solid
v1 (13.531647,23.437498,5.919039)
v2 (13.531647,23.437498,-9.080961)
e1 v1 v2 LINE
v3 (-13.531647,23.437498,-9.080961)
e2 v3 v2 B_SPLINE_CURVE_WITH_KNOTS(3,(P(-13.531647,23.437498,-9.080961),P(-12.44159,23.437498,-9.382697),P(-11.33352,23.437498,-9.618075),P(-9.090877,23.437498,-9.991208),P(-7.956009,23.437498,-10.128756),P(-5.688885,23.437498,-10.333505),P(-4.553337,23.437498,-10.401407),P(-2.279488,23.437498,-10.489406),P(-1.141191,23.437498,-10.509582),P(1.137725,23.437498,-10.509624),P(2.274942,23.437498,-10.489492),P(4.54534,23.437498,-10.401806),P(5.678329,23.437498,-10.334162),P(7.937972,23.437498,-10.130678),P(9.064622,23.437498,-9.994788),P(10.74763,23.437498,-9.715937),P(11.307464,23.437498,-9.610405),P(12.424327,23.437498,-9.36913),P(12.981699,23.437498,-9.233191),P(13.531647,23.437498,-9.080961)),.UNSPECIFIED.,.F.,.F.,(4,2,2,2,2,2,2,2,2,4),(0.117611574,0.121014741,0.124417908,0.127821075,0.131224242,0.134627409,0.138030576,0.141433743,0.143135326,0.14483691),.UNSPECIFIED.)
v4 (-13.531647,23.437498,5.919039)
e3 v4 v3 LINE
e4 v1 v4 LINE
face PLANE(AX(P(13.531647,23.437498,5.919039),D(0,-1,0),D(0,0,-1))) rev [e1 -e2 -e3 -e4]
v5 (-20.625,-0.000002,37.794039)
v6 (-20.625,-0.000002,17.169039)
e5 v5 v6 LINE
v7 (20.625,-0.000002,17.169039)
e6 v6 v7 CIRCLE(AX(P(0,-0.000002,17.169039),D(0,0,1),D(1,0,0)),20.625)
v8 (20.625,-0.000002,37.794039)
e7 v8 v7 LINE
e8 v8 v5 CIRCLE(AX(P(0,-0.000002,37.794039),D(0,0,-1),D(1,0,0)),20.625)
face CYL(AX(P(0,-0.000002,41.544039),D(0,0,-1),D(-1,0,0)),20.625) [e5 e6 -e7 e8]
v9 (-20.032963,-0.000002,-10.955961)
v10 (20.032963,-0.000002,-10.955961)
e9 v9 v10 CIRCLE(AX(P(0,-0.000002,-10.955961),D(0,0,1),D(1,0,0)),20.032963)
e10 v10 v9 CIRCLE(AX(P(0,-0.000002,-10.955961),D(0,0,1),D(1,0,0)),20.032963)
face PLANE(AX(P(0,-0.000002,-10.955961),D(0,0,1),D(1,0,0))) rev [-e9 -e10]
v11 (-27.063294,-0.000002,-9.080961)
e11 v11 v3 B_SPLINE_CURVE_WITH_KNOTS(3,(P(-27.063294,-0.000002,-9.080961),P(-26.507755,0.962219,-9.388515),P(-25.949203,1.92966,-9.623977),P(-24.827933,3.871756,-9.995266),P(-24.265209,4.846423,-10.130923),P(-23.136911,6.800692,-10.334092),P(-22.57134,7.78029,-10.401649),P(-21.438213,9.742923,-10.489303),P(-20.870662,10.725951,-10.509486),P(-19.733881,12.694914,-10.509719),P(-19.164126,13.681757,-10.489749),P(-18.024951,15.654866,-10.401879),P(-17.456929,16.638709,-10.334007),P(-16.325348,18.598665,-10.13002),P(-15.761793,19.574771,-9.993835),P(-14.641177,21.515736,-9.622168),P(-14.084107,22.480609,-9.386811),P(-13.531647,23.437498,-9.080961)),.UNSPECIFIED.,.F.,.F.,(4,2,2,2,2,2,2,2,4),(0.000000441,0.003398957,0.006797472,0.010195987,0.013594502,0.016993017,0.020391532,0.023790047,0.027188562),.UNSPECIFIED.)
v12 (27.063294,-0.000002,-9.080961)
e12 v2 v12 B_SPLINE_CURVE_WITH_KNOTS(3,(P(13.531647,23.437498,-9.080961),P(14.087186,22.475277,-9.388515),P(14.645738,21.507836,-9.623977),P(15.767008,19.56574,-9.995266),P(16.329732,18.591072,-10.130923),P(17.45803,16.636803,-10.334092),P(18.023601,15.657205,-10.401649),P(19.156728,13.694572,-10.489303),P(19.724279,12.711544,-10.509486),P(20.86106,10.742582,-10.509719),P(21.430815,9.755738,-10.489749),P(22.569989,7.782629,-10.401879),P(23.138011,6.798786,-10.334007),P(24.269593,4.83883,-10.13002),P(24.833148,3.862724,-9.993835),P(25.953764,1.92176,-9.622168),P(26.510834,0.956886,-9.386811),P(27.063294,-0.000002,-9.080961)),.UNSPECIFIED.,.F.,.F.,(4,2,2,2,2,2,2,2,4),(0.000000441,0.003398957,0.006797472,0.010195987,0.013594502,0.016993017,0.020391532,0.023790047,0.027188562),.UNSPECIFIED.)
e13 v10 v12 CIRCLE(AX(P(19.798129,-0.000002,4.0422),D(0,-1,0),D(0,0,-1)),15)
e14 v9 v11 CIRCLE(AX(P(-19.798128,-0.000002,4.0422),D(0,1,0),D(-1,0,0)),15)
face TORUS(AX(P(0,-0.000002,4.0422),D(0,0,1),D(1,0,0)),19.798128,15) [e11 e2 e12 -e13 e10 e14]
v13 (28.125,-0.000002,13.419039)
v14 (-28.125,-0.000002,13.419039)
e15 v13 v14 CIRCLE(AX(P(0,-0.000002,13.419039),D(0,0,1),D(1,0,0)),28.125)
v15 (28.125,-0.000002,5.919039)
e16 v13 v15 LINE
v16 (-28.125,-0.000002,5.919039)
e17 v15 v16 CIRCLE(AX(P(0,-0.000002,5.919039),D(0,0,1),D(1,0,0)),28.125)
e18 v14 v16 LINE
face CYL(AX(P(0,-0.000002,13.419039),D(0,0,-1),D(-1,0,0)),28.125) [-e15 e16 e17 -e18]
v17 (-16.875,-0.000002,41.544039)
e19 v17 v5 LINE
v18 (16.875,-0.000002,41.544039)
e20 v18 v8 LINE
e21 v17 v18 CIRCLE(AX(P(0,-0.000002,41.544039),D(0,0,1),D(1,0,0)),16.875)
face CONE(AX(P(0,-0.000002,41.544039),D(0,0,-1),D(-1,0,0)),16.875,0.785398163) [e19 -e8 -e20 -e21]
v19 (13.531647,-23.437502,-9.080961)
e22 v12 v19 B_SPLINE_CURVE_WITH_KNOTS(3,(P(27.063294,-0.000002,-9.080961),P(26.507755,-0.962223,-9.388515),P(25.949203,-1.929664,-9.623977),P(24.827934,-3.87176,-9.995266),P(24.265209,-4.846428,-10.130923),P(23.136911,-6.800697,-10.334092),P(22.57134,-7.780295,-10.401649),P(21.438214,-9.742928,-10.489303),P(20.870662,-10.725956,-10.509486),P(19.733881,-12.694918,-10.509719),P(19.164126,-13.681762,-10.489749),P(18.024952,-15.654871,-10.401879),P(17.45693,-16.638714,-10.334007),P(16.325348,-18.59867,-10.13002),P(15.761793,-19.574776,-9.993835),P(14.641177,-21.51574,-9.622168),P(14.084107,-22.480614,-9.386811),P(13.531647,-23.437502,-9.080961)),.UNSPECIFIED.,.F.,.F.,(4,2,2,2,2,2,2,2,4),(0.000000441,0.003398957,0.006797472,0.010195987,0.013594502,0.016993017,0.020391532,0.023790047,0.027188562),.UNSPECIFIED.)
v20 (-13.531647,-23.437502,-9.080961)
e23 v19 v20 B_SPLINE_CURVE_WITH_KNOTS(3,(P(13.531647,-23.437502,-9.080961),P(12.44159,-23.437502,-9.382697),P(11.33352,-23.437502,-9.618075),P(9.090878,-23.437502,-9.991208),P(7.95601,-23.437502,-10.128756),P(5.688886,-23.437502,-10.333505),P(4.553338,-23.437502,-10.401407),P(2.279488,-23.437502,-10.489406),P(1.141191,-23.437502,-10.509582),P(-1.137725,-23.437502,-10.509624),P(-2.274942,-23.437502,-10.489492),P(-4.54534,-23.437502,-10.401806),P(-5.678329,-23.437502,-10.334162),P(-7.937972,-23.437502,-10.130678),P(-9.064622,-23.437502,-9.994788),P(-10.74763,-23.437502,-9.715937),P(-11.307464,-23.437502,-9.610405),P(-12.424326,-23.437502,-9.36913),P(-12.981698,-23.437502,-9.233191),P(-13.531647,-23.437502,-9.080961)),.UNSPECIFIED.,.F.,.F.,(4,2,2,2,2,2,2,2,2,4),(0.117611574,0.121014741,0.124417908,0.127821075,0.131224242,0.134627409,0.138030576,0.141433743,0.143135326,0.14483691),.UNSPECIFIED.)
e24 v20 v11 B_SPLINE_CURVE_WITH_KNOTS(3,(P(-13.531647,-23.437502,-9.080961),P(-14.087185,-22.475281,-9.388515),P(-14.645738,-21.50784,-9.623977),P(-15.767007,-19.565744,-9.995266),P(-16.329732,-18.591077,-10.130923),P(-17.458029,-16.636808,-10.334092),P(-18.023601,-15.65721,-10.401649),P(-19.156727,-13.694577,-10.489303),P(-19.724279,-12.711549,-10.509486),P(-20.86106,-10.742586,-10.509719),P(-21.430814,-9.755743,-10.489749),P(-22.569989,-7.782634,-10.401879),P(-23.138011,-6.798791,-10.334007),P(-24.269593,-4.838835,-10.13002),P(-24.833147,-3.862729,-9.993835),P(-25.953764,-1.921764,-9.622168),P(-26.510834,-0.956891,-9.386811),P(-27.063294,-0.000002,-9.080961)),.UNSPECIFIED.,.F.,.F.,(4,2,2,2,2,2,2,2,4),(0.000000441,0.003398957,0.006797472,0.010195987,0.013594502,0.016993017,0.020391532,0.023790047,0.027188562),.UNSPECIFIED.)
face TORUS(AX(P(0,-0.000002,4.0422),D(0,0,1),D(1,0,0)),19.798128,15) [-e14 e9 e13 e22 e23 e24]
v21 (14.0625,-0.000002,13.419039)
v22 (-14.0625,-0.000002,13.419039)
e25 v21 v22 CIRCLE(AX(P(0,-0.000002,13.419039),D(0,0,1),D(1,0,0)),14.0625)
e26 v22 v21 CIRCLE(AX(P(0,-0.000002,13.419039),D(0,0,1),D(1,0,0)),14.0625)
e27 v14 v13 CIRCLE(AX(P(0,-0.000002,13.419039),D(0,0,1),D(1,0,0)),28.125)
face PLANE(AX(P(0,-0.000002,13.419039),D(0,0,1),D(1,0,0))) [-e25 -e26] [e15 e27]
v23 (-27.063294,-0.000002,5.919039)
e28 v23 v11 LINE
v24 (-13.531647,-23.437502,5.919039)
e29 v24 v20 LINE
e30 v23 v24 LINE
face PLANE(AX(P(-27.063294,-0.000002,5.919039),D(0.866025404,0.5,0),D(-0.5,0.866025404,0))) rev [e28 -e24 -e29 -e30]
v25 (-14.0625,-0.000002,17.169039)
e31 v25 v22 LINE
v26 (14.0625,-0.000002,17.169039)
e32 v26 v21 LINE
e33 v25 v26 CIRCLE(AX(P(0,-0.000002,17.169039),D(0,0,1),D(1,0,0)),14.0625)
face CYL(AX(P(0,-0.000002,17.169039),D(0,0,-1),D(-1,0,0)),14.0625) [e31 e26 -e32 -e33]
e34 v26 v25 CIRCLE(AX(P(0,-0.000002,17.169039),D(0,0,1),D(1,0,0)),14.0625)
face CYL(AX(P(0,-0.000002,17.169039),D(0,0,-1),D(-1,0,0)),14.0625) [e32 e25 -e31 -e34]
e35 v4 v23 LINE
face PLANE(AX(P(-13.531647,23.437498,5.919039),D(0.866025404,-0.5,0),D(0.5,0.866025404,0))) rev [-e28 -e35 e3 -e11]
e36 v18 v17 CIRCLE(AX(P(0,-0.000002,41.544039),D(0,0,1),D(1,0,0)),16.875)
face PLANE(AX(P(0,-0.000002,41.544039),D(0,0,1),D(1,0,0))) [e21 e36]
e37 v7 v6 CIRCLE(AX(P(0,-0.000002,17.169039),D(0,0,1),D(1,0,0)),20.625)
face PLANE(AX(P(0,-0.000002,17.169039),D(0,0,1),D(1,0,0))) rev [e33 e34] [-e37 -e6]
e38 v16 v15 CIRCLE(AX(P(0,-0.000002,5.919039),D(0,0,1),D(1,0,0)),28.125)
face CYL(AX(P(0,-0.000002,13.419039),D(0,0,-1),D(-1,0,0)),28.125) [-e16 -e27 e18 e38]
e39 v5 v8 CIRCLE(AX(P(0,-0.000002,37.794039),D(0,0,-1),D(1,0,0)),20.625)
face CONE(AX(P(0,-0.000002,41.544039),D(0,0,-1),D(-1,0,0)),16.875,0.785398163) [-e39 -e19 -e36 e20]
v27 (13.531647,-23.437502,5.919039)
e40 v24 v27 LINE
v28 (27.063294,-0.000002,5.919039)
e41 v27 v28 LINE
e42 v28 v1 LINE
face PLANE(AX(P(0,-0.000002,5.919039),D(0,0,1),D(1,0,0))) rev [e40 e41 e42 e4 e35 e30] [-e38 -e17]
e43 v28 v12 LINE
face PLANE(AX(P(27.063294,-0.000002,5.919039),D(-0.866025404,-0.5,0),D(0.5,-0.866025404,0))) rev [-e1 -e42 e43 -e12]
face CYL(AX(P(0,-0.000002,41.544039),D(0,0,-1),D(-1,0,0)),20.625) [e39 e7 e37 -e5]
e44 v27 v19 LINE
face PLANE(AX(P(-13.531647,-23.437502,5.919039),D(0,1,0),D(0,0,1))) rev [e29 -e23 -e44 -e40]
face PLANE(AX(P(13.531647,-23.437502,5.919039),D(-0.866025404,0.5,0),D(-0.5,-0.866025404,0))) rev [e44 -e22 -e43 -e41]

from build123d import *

# Parameters (mm, degrees)
BOSS_EXTRUDE1_DEPTH = 9
SKETCH2_R           = 15
BOSS_EXTRUDE2_DEPTH = 4
SKETCH3_R           = 7.5
BOSS_EXTRUDE3_DEPTH = 2
SKETCH4_R           = 11
BOSS_EXTRUDE5_DEPTH = 13
CHAMFER1_SIZE       = 2
SCALE_1_SCALE       = 1.875


with BuildPart() as part:
    # Sketch1 → Boss-Extrude1 (new body)
    with BuildSketch(Plane.XY):
        Polygon((14.43375673, 0), (7.216878365, 12.5), (-7.216878365, 12.5), (-14.43375673, 0), (-7.216878365, -12.5), (7.216878365, -12.5), align=None)
    extrude(amount=BOSS_EXTRUDE1_DEPTH)

    # Sketch2 → Boss-Extrude2 (add)
    with BuildSketch(Plane.XY.offset(9)):
        Circle(SKETCH2_R)
    extrude(amount=BOSS_EXTRUDE2_DEPTH)

    # Sketch3 → Boss-Extrude3 (add)
    with BuildSketch(Plane.XY.offset(13)):
        Circle(SKETCH3_R)
    extrude(amount=BOSS_EXTRUDE3_DEPTH)

    # Sketch4 → Boss-Extrude5 (add)
    with BuildSketch(Plane.XY.offset(15)):
        with Locations(Location((0, 0, 0), (0, 0, 180))):
            Circle(SKETCH4_R)
    extrude(amount=BOSS_EXTRUDE5_DEPTH)

    # Chamfer1
    chamfer1_edges = [part.edges().sort_by_distance(p)[0] for p in [
        (11, 0, 28),
    ]]
    chamfer(chamfer1_edges, length=CHAMFER1_SIZE)

    # Sketch6 → Cut-Revolve4 (revolve, cut)
    with BuildSketch(Plane(origin=(0, 0, 0), x_dir=(1, 0, 0), z_dir=(0, 1, 0)), mode=Mode.PRIVATE) as cut_revolve4_sk:
        with BuildLine():
            Line((-10.43375673, 0), (-11.300713231, 3.45481125))
            Line((-11.300713231, 3.45481125), (-14.43375673, 0))
            Line((-14.43375673, 0), (-14.43375673, -1))
            ThreePointArc((-14.43375673, -1), (-12.499286844, -0.237879543), (-10.43375673, 0))
        make_face()
    revolve(cut_revolve4_sk.sketch.rotate(Axis((0, 0, 0), (0, 0, -1)), 180), axis=Axis((0, 0, 0), (0, 0, -1)), mode=Mode.SUBTRACT)


with BuildPart() as part_1:
    # Scale 1: scaled about (-3.1e-08, 2.41e-07, 12.521211358)
    add(part.part.scale(SCALE_1_SCALE).moved(Location((2.7e-08, -2.11e-07, -10.956059938))))


solid = part_1.part
